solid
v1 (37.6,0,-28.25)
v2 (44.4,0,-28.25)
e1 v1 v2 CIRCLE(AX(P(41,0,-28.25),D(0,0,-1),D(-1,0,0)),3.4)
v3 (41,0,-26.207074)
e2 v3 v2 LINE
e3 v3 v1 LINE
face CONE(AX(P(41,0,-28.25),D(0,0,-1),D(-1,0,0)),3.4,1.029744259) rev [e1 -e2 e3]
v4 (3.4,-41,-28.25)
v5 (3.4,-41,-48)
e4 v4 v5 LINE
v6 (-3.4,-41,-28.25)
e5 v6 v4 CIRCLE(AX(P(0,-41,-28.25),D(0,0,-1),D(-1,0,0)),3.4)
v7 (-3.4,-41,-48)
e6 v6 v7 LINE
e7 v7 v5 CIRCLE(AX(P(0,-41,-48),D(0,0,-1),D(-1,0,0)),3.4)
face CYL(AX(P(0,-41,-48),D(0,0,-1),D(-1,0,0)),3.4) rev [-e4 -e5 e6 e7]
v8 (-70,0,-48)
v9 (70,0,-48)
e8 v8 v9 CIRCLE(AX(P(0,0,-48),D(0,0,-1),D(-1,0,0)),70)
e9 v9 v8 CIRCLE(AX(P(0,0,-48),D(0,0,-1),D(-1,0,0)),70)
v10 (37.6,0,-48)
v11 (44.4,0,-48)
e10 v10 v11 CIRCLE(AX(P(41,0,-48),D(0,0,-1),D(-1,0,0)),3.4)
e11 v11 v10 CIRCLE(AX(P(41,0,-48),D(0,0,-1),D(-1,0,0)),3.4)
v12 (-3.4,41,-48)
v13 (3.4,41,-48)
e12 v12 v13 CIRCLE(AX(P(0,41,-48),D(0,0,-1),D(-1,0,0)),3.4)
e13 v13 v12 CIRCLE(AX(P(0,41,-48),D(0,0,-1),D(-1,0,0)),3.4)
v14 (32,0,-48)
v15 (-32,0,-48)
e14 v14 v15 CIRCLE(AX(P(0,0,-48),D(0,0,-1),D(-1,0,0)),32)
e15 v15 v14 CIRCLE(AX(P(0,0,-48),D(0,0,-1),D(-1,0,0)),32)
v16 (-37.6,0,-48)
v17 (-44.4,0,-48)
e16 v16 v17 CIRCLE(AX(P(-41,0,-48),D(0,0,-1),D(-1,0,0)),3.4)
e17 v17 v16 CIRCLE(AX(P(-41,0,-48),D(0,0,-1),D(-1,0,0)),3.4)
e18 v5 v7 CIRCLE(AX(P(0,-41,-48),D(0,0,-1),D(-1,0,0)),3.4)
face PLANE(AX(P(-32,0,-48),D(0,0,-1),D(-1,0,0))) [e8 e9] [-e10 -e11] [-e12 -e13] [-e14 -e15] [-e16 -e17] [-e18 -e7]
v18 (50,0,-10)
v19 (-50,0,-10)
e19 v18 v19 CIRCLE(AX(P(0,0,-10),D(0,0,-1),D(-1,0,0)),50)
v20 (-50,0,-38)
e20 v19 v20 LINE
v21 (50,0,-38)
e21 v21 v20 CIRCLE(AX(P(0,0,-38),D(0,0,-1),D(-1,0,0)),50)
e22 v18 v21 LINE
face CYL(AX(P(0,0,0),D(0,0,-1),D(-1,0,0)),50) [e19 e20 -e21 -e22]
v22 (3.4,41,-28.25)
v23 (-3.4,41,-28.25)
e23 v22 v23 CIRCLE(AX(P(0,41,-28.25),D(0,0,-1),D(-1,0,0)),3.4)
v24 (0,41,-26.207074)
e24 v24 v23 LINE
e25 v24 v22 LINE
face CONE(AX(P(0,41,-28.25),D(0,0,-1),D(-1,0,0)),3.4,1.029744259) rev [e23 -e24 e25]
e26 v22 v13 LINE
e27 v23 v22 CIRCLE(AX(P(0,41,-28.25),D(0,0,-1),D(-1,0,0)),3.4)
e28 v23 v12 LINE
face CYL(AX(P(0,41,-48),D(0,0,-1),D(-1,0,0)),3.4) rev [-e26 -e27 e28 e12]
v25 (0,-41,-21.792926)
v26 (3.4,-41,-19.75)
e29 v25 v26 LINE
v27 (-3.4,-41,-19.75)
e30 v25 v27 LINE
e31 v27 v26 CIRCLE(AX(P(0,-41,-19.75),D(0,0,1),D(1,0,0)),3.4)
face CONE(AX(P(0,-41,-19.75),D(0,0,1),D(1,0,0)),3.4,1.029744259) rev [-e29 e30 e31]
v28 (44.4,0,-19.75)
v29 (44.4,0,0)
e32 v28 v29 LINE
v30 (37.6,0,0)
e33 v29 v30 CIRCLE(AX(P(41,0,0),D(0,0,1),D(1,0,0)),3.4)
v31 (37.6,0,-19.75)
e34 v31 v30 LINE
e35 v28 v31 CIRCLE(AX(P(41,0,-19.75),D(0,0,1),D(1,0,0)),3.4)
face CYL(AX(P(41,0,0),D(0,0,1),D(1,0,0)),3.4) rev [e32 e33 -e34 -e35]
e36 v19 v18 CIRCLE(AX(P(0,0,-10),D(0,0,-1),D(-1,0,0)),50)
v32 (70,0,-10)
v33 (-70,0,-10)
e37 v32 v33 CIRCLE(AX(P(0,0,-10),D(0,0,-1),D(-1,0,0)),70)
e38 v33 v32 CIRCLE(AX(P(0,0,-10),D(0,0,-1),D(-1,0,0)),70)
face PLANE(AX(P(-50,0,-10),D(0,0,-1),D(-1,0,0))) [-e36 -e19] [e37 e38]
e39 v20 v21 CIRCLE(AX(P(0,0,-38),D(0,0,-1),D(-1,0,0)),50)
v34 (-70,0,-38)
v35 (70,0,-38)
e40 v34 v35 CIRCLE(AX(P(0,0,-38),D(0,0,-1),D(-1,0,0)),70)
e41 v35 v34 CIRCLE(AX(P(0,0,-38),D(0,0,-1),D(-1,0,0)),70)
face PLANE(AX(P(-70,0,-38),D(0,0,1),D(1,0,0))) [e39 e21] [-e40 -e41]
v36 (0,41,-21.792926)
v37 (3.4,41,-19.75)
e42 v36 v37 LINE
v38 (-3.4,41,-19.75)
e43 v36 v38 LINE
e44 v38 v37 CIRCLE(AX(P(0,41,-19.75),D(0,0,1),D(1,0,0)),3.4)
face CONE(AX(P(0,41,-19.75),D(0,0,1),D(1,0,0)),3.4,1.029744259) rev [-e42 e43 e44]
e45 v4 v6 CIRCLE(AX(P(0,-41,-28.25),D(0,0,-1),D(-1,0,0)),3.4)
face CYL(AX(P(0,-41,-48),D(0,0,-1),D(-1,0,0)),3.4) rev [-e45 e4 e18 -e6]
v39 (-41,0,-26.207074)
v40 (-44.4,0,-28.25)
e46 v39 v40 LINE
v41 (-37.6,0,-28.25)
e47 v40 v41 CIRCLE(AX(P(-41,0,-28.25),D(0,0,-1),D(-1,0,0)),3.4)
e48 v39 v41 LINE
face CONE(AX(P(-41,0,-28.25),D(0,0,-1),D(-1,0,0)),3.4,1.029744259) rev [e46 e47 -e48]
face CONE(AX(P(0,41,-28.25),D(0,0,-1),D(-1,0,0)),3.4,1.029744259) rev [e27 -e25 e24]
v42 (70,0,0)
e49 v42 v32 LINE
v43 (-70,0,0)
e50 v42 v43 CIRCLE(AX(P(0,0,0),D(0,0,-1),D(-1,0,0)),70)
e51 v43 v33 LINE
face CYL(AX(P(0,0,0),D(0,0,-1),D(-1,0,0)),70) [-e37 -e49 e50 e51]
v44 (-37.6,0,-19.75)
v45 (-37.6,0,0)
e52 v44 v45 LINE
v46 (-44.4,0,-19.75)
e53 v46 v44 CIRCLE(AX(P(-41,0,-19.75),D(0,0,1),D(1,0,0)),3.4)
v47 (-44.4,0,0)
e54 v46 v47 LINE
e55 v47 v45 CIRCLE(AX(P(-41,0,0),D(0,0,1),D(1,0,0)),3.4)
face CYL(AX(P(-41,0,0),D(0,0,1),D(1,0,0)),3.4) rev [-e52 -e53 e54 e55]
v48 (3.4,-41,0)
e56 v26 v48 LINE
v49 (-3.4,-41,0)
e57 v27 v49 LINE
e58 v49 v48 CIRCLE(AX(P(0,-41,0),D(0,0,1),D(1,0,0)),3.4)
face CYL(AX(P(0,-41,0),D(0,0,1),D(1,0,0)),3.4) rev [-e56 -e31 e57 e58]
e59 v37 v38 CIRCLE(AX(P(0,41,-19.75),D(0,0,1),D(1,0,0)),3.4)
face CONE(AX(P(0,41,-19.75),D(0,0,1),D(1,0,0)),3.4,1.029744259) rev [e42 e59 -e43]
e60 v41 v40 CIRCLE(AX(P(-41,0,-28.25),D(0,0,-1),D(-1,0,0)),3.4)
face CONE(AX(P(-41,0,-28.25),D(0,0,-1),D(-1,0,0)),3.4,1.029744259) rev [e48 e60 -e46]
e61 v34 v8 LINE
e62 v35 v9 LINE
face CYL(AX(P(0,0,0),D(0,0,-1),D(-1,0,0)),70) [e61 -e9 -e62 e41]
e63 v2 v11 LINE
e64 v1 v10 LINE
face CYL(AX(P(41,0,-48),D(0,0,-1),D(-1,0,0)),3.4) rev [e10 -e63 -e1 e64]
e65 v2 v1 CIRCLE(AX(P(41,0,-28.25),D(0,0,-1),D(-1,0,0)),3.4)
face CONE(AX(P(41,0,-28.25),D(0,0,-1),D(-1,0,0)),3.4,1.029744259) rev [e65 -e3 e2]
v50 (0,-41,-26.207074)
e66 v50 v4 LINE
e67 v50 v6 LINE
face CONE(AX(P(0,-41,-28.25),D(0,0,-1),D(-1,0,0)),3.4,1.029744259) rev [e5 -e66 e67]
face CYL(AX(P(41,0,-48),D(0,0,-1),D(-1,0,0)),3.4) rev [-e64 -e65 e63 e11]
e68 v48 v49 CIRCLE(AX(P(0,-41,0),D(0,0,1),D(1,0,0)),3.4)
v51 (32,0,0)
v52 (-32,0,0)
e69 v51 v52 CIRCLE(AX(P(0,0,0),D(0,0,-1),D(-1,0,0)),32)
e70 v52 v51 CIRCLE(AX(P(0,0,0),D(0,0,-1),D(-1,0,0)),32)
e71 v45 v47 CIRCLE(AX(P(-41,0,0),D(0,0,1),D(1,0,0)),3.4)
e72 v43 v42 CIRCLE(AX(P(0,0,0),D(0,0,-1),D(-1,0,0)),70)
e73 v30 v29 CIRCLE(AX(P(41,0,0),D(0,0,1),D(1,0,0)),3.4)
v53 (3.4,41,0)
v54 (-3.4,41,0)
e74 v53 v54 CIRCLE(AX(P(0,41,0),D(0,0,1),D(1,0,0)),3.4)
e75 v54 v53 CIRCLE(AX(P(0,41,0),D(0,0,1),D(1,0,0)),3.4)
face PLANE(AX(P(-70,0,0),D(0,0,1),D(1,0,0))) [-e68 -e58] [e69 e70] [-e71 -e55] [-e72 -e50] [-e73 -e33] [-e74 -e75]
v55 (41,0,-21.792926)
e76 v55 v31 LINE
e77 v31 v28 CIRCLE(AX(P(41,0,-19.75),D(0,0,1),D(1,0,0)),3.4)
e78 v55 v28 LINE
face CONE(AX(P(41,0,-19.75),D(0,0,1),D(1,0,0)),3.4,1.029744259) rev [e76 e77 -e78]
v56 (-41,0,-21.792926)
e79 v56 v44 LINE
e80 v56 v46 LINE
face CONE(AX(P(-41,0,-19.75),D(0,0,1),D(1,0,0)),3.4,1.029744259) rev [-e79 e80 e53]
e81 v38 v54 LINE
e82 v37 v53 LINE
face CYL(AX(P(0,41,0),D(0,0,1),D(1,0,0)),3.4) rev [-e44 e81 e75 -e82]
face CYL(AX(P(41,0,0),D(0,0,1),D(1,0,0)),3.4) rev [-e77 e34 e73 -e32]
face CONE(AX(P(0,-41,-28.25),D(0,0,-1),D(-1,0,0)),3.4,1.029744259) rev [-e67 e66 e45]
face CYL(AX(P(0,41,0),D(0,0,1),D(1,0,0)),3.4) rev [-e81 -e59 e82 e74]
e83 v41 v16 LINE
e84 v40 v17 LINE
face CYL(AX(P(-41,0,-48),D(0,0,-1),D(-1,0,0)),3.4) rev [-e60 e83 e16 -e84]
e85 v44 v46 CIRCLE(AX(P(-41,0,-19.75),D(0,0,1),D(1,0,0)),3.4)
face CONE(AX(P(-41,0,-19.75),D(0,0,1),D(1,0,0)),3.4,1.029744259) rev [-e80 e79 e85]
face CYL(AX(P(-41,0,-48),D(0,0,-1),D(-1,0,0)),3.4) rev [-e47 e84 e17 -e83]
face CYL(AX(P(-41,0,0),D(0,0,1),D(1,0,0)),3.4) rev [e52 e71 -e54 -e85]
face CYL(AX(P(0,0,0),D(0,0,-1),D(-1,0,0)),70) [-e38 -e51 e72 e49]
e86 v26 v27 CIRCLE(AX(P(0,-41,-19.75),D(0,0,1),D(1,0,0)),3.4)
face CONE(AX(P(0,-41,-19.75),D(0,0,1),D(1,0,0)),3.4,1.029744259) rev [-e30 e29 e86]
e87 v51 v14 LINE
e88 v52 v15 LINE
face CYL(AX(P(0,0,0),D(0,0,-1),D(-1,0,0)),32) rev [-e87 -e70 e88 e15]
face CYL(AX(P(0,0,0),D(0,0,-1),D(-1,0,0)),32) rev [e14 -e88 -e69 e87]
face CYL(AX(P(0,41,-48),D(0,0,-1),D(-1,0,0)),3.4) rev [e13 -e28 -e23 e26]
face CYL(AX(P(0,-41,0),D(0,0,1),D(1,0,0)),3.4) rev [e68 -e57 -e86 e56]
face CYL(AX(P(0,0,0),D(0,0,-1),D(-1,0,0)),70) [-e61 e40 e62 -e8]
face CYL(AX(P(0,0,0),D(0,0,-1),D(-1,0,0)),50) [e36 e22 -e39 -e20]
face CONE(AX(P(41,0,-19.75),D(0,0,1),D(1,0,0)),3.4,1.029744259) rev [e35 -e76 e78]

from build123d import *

# Parameters (mm, degrees)
HOLE_WIZARD_M8_1_D     = 6.8
HOLE_WIZARD_M8_1_DEPTH = 19.75
HOLE_WIZARD_M8_1_TIP   = 2.042926105
HOLE_WIZARD_M8_3_D     = 6.8
HOLE_WIZARD_M8_3_DEPTH = 19.75
HOLE_WIZARD_M8_3_TIP   = 2.042926105


with BuildPart() as part:
    # 草图1 → 旋转1 (revolve)
    with BuildSketch(Plane(origin=(0, 0, 0), x_dir=(1, 0, 0), z_dir=(0, 1, 0))):
        Polygon((-32, 48), (-70, 48), (-70, 38), (-50, 38), (-50, 10), (-70, 10), (-70, 0), (-32, 0), align=None)
    revolve(axis=Axis((0, 0, 0), (0, 0, 1)))

    # M8 螺纹孔1
    with Locations(Plane(origin=(0, 0, -48), x_dir=(-1, 0, 0), z_dir=(0, 0, -1))):
        with Locations((0, 41), (41, 0), (-41, 0), (0, -41)):
            Hole(HOLE_WIZARD_M8_1_D / 2, depth=HOLE_WIZARD_M8_1_DEPTH)
            with Locations((0, 0, -(HOLE_WIZARD_M8_1_DEPTH + HOLE_WIZARD_M8_1_TIP / 2))):  # 118° drill point
                Cone(0, HOLE_WIZARD_M8_1_D / 2, HOLE_WIZARD_M8_1_TIP, mode=Mode.SUBTRACT)

    # M8 螺纹孔3
    with Locations(Plane.XY):
        with Locations((41, 0), (0, -41), (-41, 0), (0, 41)):
            Hole(HOLE_WIZARD_M8_3_D / 2, depth=HOLE_WIZARD_M8_3_DEPTH)
            with Locations((0, 0, -(HOLE_WIZARD_M8_3_DEPTH + HOLE_WIZARD_M8_3_TIP / 2))):  # 118° drill point
                Cone(0, HOLE_WIZARD_M8_3_D / 2, HOLE_WIZARD_M8_3_TIP, mode=Mode.SUBTRACT)


solid = part.part
